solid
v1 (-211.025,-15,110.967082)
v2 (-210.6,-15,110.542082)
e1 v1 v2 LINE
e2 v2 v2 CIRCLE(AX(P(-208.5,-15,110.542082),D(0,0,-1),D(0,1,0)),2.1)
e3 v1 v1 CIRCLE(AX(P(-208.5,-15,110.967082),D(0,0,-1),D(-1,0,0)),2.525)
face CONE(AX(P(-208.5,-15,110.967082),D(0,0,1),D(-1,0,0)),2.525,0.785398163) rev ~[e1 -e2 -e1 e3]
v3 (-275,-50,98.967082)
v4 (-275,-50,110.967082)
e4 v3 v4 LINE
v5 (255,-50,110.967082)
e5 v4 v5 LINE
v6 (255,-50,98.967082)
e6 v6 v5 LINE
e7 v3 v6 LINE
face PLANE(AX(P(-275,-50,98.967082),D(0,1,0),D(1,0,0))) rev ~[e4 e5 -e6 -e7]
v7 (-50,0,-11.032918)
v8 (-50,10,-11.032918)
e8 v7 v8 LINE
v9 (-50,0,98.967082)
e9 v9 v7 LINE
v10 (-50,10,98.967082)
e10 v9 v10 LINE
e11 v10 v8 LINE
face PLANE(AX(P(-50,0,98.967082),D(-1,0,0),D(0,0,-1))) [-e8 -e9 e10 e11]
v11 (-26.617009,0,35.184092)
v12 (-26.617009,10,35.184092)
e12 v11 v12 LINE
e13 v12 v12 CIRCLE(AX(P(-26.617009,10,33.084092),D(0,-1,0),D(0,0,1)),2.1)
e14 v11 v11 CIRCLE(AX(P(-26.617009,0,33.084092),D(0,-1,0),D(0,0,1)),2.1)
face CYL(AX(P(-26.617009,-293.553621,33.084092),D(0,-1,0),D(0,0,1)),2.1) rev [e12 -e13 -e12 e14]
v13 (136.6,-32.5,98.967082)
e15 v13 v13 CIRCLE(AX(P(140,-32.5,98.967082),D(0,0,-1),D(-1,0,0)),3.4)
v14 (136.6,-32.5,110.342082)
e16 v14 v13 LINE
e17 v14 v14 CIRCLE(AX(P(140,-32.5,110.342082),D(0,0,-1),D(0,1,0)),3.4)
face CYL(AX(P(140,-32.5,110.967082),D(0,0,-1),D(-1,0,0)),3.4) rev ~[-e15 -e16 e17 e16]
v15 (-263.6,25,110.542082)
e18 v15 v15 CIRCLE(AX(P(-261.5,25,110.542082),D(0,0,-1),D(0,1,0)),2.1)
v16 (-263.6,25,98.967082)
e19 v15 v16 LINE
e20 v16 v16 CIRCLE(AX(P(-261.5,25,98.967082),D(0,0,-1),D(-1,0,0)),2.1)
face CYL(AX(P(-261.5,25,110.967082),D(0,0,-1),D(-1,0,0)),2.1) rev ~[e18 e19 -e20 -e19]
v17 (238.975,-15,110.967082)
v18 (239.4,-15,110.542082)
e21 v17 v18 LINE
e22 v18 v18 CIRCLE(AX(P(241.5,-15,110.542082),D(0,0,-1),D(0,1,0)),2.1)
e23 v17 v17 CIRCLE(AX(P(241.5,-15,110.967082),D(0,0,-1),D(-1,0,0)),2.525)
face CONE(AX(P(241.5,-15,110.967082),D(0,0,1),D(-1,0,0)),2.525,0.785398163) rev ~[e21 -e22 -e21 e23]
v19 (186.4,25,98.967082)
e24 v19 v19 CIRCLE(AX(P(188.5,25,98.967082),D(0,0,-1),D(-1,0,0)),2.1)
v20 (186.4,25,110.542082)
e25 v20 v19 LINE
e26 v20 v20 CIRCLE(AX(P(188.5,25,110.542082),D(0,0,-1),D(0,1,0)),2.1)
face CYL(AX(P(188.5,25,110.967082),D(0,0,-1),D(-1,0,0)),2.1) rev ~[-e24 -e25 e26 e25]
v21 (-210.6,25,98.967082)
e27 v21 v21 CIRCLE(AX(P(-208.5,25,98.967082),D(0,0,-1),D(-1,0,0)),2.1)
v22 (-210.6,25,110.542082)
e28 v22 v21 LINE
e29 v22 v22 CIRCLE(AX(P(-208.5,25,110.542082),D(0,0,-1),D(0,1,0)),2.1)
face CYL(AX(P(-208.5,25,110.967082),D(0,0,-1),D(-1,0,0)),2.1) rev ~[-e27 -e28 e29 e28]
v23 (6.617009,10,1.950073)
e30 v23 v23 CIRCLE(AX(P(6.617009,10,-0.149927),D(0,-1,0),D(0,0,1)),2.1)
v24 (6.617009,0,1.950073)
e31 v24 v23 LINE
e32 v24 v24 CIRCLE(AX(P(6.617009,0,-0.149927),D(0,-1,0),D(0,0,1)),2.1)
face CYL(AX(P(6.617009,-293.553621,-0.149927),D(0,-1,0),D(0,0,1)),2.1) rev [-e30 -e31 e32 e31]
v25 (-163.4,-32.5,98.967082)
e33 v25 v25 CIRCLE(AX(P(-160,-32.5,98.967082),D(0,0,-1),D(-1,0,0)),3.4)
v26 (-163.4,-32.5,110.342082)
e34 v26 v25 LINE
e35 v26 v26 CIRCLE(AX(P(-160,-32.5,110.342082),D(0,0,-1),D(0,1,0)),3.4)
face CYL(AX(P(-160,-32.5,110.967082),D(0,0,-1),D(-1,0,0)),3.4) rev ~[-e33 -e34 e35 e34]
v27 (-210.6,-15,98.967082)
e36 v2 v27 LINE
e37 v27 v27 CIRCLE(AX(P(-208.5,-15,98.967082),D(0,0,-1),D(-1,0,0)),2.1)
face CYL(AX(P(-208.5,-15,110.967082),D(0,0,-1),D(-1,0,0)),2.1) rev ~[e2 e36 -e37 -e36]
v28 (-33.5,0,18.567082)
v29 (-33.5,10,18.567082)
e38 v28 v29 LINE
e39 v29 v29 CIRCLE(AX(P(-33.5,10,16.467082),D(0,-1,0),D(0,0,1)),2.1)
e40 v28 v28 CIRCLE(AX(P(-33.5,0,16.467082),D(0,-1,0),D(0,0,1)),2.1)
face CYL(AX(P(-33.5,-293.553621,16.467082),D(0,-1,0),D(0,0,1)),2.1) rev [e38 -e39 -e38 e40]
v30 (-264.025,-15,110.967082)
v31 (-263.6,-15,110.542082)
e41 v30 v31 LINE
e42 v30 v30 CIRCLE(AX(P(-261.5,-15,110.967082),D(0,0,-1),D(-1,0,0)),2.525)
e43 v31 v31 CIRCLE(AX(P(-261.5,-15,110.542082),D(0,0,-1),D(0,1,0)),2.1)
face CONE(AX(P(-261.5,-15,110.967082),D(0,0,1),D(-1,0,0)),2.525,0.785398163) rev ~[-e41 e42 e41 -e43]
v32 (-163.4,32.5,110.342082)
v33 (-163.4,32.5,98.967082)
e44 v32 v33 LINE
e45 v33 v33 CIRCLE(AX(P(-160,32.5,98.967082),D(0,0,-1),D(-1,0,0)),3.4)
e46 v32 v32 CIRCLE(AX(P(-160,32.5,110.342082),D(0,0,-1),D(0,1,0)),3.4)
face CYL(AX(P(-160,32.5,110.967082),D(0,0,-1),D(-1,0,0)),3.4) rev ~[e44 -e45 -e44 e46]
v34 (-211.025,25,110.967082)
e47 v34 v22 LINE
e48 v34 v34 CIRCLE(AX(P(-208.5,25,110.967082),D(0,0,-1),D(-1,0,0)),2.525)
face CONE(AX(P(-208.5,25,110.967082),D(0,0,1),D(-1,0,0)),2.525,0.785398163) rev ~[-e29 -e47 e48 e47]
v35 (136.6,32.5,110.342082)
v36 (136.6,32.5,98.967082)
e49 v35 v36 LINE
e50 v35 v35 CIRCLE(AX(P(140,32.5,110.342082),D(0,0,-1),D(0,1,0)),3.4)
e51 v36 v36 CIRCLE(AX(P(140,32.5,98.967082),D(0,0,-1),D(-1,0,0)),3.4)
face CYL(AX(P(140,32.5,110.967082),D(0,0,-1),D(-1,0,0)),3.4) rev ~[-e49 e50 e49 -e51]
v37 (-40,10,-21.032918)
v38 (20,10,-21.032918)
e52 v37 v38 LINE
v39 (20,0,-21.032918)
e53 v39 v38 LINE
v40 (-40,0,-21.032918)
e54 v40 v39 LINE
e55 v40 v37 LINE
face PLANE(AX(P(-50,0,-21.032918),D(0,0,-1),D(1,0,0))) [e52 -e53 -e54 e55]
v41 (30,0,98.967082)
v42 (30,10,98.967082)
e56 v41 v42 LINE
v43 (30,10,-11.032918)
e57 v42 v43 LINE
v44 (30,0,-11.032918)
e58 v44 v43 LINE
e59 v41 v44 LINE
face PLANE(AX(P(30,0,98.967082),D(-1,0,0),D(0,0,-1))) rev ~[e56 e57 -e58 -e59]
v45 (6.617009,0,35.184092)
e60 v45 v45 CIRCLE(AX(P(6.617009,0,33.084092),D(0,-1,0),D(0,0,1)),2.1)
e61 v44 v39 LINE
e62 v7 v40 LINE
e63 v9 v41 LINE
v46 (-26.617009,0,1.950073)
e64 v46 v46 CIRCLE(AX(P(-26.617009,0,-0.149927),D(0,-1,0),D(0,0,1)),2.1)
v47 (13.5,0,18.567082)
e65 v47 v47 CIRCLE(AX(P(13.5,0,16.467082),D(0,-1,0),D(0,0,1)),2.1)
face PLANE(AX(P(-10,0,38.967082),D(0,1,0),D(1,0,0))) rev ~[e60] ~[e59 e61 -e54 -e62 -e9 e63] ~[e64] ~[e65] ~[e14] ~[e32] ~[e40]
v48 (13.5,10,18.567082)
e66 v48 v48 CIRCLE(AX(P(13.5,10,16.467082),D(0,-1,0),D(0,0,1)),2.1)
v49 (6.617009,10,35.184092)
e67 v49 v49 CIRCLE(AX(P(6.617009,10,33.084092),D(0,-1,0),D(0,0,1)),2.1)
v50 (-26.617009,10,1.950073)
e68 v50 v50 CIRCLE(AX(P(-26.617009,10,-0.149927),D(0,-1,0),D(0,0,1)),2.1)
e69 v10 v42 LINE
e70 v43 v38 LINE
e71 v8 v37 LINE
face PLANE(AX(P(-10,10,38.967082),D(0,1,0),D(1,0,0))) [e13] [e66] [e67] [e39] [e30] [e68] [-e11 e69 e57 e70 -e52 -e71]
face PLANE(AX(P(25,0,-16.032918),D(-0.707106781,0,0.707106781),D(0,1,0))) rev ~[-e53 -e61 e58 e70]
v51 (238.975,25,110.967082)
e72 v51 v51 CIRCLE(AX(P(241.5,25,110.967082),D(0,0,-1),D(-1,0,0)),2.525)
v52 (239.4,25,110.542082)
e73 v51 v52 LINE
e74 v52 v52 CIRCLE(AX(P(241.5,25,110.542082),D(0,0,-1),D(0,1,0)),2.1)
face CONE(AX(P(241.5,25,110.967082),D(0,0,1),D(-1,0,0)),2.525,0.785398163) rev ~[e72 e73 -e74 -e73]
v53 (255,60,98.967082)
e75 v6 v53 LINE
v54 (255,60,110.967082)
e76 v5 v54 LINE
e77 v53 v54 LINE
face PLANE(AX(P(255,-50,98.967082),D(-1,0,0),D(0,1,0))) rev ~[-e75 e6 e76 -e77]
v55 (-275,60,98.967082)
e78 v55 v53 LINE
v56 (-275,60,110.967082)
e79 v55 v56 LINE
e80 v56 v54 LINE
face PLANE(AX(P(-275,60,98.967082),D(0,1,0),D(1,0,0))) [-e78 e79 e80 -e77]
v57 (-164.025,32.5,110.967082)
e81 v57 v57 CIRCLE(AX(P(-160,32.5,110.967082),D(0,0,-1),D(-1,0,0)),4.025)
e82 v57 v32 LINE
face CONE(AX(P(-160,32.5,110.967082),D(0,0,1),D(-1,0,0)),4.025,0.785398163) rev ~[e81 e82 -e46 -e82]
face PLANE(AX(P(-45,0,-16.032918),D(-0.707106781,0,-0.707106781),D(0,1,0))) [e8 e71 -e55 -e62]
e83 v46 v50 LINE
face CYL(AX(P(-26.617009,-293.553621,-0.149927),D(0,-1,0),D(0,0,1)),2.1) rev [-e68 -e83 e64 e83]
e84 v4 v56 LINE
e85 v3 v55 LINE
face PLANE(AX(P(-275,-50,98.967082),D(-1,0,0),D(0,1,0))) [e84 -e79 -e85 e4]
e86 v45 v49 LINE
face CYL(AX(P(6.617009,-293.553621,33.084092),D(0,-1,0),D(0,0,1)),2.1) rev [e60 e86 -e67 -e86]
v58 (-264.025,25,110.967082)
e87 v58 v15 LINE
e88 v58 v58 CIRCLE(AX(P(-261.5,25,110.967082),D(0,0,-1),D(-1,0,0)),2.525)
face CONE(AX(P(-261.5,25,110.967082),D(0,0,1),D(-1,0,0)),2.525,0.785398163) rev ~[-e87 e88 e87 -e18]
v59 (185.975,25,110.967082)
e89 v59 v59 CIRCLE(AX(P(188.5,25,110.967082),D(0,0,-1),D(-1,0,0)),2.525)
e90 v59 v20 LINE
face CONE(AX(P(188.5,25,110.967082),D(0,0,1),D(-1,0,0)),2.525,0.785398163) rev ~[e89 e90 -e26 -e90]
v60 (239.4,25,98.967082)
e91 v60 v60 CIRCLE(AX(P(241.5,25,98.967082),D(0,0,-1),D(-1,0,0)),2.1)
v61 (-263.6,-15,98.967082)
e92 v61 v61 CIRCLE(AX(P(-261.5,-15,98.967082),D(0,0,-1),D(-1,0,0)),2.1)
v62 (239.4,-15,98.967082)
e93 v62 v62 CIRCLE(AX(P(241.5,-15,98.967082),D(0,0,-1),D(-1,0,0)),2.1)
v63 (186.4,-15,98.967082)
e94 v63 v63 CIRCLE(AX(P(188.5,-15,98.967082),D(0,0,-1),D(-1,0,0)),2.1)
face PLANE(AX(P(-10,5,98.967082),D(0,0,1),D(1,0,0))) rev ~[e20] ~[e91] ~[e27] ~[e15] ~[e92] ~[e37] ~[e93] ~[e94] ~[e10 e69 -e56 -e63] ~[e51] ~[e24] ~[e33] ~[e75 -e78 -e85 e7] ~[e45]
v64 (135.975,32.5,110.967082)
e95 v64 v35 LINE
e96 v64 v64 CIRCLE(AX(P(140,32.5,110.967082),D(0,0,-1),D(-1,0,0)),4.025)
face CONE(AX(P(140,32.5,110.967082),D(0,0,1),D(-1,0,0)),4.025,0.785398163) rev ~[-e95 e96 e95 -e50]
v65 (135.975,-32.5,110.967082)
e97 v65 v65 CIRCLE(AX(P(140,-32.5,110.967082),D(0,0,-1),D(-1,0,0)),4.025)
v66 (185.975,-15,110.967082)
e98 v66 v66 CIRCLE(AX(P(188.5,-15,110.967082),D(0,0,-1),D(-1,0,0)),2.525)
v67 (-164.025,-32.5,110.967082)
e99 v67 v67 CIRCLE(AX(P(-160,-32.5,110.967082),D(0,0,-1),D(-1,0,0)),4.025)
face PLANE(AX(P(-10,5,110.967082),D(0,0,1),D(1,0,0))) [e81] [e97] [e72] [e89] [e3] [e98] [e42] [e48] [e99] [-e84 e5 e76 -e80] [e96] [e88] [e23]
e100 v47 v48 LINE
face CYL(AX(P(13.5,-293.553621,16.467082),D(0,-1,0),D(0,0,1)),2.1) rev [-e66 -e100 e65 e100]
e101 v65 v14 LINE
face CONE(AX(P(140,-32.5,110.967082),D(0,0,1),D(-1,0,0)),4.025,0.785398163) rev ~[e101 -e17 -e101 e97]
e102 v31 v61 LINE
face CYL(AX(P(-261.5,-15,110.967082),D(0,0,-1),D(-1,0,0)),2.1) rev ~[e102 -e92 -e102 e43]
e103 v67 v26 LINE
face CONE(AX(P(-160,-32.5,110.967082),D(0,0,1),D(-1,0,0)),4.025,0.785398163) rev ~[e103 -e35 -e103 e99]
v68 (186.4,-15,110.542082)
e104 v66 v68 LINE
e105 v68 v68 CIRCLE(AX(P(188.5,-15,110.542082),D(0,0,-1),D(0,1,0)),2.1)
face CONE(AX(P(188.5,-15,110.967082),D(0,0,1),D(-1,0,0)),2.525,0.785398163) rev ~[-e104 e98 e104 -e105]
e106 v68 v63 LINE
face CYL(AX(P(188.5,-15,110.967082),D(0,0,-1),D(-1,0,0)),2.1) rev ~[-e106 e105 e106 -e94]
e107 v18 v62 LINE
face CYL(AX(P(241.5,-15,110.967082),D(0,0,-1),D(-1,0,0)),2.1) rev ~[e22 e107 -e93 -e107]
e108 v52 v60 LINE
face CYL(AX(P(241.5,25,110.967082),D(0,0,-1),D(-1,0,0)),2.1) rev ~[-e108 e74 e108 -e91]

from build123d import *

# Parameters (mm, degrees)
SKETCH1_W                   = 80
SKETCH1_H                   = 120
BOSS_EXTRUDE1_DEPTH         = 10
SKETCH2_W                   = 530
SKETCH2_H                   = 110
BOSS_EXTRUDE2_DEPTH         = 12
CHAMFER1_SIZE               = 10
CUT_EXTRUDE1_DEPTH          = 303.553620593
CUT_EXTRUDE1_DEPTH_BACK     = 303.553620593
SKETCH3_R                   = 2.1
M5_TAPPED_HOLE1_D           = 4.2
M5_TAPPED_HOLE1_DEPTH       = 12.4
M5_TAPPED_HOLE1_CSINK_D     = 5.05
M5_TAPPED_HOLE1_CSINK_ANGLE = 90
M5_TAPPED_HOLE1_TIP         = 1.2618073
M8_TAPPED_HOLE1_D           = 6.8
M8_TAPPED_HOLE1_DEPTH       = 22.25
M8_TAPPED_HOLE1_CSINK_D     = 8.05
M8_TAPPED_HOLE1_CSINK_ANGLE = 90
M8_TAPPED_HOLE1_TIP         = 2.042926105


with BuildPart() as part:
    # Sketch1 → Boss-Extrude1 (new body)
    with BuildSketch(Plane(origin=(0, 0, 0), x_dir=(1, 0, 0), z_dir=(0, 1, 0))):
        with Locations((-10, -38.967082208)):
            Rectangle(SKETCH1_W, SKETCH1_H)
    extrude(amount=BOSS_EXTRUDE1_DEPTH)

    # Sketch2 → Boss-Extrude2 (add)
    with BuildSketch(Plane.XY.offset(98.967082208)):
        with Locations((-10, 5)):
            Rectangle(SKETCH2_W, SKETCH2_H)
    extrude(amount=BOSS_EXTRUDE2_DEPTH)

    # Chamfer1
    chamfer1_edges = [part.edges().sort_by_distance(p)[0] for p in [
        (-50, 5, -21.032917792),
        (30, 5, -21.032917792),
    ]]
    chamfer(chamfer1_edges, length=CHAMFER1_SIZE)

    # Sketch3 → Cut-Extrude1 (cut, two sides: drawn at the far end of the back side and taken through both)
    with BuildSketch(Plane(origin=(0, 10, 0), x_dir=(1, 0, 0), z_dir=(0, 1, 0)).offset(-CUT_EXTRUDE1_DEPTH_BACK)):
        with Locations(Location((6.617009358, 0.14992715, 0), (0, 0, 270))):
            Circle(SKETCH3_R)
        with Locations(Location((13.499999853, -16.467082208, 0), (0, 0, 270))):
            Circle(SKETCH3_R)
        with Locations(Location((6.617009358, -33.084091566, 0), (0, 0, 270))):
            Circle(SKETCH3_R)
        with Locations(Location((-26.617009358, -33.084091566, 0), (0, 0, 270))):
            Circle(SKETCH3_R)
        with Locations(Location((-33.499999853, -16.467082208, 0), (0, 0, 270))):
            Circle(SKETCH3_R)
        with Locations(Location((-26.617009358, 0.14992715, 0), (0, 0, 270))):
            Circle(SKETCH3_R)
    extrude(amount=CUT_EXTRUDE1_DEPTH + CUT_EXTRUDE1_DEPTH_BACK, mode=Mode.SUBTRACT)

    # M5 Tapped Hole1
    with Locations(Plane.XY.offset(110.967082208)):
        with Locations((-261.5, 25), (-261.5, -15), (-208.5, 25), (-208.5, -15), (188.5, -15), (188.5, 25), (241.5, -15), (241.5, 25)):
            CounterSinkHole(M5_TAPPED_HOLE1_D / 2, M5_TAPPED_HOLE1_CSINK_D / 2, depth=M5_TAPPED_HOLE1_DEPTH, counter_sink_angle=M5_TAPPED_HOLE1_CSINK_ANGLE)
            with Locations((0, 0, -(M5_TAPPED_HOLE1_DEPTH + M5_TAPPED_HOLE1_TIP / 2))):  # 118° drill point
                Cone(0, M5_TAPPED_HOLE1_D / 2, M5_TAPPED_HOLE1_TIP, mode=Mode.SUBTRACT)

    # M8 Tapped Hole1
    with Locations(Plane.XY.offset(110.967082208)):
        with Locations((-160, 32.5), (-160, -32.5), (140, 32.5), (140, -32.5)):
            CounterSinkHole(M8_TAPPED_HOLE1_D / 2, M8_TAPPED_HOLE1_CSINK_D / 2, depth=M8_TAPPED_HOLE1_DEPTH, counter_sink_angle=M8_TAPPED_HOLE1_CSINK_ANGLE)
            with Locations((0, 0, -(M8_TAPPED_HOLE1_DEPTH + M8_TAPPED_HOLE1_TIP / 2))):  # 118° drill point
                Cone(0, M8_TAPPED_HOLE1_D / 2, M8_TAPPED_HOLE1_TIP, mode=Mode.SUBTRACT)


solid = part.part
